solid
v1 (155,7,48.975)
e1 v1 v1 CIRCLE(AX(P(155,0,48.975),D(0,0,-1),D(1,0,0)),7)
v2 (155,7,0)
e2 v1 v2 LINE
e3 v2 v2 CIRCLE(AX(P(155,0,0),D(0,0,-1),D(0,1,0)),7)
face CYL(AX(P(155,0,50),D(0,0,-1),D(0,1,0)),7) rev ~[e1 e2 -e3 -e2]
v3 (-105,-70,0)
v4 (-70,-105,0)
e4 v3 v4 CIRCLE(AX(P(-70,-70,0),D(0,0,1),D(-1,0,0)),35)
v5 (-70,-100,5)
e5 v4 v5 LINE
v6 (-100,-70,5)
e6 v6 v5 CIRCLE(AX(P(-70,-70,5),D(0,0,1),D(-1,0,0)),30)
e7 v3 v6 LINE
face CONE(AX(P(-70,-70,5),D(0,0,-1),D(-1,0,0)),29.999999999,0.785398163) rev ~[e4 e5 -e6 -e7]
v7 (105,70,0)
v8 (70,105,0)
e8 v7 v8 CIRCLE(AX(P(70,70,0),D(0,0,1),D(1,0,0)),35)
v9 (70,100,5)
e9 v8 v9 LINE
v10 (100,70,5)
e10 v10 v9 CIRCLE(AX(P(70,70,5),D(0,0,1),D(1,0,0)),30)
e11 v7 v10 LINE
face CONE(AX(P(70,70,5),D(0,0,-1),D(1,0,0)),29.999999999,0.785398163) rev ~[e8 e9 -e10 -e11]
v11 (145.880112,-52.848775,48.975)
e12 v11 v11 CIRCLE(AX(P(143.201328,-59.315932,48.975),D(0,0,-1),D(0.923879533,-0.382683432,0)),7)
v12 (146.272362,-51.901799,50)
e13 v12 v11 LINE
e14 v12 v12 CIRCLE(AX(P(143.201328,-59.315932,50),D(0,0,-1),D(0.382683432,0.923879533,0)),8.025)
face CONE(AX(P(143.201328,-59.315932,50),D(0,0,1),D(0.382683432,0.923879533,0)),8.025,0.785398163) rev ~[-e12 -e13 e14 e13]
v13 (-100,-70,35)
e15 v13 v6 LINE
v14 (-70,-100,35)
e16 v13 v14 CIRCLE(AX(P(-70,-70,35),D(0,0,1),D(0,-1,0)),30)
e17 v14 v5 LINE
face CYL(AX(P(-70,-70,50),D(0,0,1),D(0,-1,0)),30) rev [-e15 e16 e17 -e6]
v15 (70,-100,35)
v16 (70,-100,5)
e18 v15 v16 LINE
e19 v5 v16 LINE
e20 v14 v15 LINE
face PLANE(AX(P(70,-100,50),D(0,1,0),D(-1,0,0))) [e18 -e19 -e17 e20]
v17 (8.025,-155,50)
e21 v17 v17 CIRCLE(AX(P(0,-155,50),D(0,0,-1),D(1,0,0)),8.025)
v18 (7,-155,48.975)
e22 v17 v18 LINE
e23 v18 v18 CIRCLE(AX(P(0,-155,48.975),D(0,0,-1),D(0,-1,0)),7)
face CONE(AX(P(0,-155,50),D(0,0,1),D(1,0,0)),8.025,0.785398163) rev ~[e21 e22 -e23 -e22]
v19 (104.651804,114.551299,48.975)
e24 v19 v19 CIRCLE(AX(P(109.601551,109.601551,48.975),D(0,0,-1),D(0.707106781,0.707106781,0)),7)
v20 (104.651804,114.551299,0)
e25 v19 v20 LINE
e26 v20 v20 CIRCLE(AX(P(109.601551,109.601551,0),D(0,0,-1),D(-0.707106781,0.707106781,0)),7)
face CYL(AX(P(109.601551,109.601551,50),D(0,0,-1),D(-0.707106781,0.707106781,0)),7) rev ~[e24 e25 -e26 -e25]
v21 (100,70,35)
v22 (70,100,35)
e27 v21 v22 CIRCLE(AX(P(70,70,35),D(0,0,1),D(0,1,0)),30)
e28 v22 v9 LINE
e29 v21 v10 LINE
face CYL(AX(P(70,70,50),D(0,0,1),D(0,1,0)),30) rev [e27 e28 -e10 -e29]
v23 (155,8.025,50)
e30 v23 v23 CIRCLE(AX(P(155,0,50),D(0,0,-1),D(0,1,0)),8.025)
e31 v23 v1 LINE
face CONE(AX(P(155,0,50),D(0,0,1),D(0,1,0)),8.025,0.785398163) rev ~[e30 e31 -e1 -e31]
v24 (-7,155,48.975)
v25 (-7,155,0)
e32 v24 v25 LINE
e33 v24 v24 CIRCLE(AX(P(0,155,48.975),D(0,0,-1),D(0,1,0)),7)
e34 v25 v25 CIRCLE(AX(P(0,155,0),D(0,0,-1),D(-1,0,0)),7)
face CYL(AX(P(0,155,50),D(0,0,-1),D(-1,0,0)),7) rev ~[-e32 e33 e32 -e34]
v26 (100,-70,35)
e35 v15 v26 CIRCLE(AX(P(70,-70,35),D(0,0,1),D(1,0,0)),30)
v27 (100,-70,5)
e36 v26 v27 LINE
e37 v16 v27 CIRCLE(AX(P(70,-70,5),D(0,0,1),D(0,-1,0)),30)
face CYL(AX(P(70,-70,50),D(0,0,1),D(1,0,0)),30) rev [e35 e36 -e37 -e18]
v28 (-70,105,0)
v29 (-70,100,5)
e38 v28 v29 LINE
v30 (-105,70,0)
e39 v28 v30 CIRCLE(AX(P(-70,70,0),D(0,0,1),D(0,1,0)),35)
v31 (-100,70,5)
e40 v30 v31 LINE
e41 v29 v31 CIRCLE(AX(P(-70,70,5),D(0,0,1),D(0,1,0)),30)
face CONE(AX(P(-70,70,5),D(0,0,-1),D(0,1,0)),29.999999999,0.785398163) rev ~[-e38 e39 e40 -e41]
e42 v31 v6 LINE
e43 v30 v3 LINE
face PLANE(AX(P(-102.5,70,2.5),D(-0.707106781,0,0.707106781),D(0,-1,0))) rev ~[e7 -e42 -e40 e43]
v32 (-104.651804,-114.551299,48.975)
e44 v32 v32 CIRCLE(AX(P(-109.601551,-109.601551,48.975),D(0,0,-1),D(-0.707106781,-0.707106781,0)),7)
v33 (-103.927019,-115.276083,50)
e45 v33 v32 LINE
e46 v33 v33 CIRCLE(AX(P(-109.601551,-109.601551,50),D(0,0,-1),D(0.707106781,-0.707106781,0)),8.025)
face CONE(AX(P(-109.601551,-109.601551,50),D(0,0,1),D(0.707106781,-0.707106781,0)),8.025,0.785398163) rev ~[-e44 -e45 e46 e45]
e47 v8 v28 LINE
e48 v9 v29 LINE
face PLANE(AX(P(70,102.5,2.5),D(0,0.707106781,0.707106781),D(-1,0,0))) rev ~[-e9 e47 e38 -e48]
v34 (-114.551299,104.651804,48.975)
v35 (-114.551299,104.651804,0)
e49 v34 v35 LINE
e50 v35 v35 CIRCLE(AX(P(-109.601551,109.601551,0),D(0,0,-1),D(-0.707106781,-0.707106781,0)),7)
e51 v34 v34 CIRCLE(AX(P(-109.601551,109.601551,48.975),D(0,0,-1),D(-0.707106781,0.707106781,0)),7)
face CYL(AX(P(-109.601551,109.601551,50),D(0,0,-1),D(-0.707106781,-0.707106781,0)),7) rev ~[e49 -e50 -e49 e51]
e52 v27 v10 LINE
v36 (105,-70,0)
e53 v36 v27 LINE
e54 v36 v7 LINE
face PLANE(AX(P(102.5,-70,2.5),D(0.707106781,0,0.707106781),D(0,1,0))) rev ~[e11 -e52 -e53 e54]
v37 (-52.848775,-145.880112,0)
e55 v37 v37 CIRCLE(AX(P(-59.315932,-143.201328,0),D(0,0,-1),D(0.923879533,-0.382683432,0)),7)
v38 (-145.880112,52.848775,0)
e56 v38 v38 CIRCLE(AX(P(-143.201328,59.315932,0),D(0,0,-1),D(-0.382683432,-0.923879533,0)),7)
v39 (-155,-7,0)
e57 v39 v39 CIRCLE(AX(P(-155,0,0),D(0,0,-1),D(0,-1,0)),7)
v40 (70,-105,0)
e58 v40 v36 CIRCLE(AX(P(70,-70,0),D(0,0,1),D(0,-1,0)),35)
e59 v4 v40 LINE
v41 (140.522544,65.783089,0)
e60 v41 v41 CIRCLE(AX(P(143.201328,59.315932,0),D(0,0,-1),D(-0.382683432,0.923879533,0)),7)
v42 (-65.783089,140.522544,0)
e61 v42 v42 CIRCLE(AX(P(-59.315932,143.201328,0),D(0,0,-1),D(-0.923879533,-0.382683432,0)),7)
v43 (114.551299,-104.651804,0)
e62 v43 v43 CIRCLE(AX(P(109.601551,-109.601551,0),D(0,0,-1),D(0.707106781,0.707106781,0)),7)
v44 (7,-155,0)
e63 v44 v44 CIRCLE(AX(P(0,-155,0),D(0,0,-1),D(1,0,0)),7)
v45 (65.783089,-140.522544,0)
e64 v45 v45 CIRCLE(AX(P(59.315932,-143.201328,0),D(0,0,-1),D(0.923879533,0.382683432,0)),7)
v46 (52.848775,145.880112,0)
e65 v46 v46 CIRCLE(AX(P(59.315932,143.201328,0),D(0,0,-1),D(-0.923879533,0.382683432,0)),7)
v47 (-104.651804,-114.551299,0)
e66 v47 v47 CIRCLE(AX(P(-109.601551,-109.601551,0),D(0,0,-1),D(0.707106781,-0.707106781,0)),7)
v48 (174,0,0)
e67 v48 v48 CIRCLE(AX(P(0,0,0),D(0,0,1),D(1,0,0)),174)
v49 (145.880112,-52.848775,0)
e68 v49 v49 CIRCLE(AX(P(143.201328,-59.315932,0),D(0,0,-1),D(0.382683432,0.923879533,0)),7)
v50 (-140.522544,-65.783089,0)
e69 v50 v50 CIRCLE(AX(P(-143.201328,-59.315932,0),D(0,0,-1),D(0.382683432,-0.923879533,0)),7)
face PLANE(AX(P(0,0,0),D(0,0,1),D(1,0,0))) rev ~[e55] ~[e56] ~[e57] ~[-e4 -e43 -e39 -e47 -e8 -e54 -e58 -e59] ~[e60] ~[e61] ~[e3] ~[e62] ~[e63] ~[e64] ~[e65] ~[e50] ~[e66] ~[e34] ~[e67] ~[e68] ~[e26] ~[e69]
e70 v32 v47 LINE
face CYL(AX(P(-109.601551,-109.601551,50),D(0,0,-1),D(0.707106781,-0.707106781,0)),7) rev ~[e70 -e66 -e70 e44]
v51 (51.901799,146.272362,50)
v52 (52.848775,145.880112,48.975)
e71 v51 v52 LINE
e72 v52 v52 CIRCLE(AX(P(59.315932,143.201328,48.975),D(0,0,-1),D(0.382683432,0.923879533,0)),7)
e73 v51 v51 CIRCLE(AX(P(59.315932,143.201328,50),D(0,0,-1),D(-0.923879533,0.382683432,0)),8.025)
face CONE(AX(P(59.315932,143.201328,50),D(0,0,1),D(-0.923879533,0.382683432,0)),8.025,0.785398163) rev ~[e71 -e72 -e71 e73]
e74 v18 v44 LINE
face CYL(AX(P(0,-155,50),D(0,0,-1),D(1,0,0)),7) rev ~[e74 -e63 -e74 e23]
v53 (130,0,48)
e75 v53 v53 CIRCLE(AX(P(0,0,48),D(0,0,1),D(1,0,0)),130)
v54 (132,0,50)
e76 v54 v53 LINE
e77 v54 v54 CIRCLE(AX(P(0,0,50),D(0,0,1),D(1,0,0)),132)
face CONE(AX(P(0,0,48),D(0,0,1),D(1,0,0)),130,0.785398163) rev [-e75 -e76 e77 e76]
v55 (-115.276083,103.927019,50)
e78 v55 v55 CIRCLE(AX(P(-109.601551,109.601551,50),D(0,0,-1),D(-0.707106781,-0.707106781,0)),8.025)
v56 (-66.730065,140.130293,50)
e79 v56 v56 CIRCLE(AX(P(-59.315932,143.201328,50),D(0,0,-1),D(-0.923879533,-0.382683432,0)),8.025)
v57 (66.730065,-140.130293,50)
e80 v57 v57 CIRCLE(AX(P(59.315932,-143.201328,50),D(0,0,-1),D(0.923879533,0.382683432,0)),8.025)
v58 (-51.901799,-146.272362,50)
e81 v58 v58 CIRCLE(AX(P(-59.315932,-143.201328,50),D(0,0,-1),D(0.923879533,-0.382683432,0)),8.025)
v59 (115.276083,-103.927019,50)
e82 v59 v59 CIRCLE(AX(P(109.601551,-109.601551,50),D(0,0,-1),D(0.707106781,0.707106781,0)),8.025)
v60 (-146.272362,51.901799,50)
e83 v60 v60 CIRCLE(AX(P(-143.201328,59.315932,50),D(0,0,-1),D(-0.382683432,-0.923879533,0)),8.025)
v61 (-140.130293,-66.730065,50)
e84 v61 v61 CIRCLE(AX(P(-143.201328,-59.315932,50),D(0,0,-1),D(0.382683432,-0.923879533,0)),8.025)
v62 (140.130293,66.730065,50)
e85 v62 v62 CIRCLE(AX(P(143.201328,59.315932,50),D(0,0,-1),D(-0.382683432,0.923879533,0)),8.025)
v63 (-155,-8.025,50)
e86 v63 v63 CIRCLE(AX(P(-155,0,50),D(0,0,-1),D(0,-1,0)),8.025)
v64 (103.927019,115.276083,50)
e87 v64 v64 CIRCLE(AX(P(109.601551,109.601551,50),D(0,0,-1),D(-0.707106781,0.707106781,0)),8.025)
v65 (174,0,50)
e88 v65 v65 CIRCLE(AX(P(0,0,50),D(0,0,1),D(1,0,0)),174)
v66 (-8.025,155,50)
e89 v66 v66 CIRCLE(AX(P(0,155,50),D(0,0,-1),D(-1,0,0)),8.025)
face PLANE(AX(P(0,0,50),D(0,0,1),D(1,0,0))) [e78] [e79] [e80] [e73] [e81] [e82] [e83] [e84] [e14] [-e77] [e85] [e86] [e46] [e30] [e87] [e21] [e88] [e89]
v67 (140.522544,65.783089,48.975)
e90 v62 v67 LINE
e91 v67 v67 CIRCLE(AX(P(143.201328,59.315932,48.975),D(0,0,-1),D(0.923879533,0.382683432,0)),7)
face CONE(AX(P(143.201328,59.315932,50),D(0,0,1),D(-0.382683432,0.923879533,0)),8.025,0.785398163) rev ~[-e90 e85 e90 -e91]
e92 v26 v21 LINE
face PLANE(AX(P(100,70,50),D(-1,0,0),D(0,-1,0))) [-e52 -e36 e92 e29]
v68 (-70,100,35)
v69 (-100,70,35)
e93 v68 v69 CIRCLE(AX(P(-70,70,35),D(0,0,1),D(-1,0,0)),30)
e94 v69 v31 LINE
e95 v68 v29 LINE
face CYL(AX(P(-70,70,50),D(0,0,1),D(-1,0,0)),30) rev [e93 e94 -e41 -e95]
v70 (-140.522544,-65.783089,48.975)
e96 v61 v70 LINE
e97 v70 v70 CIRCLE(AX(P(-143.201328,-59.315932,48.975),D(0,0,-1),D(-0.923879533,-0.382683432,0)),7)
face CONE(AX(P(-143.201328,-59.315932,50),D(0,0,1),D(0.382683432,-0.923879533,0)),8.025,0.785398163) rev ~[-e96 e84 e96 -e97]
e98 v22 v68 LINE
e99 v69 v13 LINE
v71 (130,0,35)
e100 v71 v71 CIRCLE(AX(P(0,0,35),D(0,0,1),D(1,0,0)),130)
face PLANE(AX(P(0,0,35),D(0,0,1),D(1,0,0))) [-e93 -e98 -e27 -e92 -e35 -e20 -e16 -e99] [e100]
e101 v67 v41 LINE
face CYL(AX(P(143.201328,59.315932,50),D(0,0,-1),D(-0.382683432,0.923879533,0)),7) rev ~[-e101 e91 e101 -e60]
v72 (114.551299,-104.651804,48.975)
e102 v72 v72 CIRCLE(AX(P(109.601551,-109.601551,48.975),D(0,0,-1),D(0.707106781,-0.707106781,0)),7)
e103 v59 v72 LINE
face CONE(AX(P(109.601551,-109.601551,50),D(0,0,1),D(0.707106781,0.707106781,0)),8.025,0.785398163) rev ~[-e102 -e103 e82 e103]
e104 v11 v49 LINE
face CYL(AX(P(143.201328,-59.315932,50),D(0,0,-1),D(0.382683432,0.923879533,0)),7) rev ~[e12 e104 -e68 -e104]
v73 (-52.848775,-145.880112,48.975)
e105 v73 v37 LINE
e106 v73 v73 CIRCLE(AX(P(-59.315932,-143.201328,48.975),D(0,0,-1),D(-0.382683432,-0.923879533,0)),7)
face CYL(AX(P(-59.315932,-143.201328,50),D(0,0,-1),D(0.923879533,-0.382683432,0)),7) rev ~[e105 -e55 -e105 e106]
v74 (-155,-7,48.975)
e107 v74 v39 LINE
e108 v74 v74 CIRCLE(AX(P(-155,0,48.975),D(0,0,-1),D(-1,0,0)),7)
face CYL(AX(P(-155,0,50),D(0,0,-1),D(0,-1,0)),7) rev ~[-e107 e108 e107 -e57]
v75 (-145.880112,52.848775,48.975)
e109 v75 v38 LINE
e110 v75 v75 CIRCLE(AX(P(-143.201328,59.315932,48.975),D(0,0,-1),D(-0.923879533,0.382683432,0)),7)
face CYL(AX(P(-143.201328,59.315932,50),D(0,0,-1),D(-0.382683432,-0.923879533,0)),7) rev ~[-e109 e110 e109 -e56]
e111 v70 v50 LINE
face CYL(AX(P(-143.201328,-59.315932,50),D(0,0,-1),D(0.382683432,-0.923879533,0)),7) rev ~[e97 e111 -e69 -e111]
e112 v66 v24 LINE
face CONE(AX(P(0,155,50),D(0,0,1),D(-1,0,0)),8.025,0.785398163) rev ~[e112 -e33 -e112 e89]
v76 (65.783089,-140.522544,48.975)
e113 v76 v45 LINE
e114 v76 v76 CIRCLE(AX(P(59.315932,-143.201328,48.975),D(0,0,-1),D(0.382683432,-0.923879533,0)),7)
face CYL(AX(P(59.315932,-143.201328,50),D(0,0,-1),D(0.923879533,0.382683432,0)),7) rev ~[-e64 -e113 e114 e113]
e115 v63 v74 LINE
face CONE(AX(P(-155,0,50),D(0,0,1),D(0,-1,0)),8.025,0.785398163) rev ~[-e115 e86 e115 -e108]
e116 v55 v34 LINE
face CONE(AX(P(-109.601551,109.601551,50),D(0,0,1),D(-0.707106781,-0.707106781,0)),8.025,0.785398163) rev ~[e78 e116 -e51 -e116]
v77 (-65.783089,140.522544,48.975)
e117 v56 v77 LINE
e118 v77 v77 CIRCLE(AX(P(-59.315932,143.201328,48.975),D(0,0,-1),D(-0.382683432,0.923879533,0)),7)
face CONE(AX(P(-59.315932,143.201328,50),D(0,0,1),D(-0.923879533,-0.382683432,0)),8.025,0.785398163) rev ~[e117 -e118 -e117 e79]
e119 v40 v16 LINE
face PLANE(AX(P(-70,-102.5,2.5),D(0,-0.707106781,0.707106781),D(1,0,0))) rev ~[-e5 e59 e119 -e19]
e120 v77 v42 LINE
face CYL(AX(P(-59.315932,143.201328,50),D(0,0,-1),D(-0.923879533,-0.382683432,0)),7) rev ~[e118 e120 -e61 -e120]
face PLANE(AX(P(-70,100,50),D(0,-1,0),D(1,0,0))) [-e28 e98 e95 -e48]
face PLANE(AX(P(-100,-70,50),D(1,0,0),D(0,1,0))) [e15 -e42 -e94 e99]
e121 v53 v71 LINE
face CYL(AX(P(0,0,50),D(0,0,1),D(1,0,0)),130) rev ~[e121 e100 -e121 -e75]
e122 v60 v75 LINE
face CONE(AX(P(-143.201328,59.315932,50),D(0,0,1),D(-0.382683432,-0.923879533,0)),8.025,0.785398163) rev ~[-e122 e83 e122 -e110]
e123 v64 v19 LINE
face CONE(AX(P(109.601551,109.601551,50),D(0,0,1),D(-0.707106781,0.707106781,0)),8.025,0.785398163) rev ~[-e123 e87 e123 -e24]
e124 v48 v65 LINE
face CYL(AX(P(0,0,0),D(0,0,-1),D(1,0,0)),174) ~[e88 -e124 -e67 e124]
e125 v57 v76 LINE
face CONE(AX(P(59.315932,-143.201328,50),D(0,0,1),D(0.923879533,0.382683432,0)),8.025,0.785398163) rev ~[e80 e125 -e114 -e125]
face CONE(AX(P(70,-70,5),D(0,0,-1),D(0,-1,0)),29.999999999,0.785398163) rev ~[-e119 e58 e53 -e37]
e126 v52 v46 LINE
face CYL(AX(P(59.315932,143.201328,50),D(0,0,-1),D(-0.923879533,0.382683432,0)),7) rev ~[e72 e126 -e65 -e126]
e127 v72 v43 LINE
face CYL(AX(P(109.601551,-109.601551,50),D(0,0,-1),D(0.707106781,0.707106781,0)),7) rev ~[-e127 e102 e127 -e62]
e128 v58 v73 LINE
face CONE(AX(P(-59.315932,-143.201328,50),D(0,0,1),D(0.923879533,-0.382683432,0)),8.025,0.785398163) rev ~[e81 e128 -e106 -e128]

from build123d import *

# Parameters (mm, degrees)
SKETCH_1_R                    = 174
EXTRUDE_1_DEPTH               = 50
CUT_EXTRUDE_1_DEPTH           = 252.101573074
HOLE_WIZARD_M16_1_D           = 14
HOLE_WIZARD_M16_1_CSINK_D     = 16.05
HOLE_WIZARD_M16_1_CSINK_ANGLE = 90
PATTERN_CIRCULAR_1_COUNT      = 16
SKETCH_5_R                    = 130
CUT_EXTRUDE_2_DEPTH           = 15
CHAMFER_1_SIZE                = 2
CHAMFER_2_SIZE                = 5


with BuildPart() as part:
    # 草图1 → 凸台-拉伸1 (new body)
    with BuildSketch(Plane.XY):
        Circle(SKETCH_1_R)
    extrude(amount=EXTRUDE_1_DEPTH)

    # 草图2 → 切除-拉伸1 (cut, through all)
    with BuildSketch(Plane.XY.offset(50)):
        with BuildLine():
            Line((-70, 100), (70, 100))
            ThreePointArc((70, 100), (91.213203436, 91.213203436), (100, 70))
            Line((100, 70), (100, -70))
            ThreePointArc((100, -70), (91.213203436, -91.213203436), (70, -100))
            Line((70, -100), (-70, -100))
            ThreePointArc((-70, -100), (-91.213203436, -91.213203436), (-100, -70))
            Line((-100, -70), (-100, 70))
            ThreePointArc((-100, 70), (-91.213203436, 91.213203436), (-70, 100))
        make_face()
    extrude(amount=-CUT_EXTRUDE_1_DEPTH, mode=Mode.SUBTRACT)

    # M16 螺纹孔1 (through all)
    with Locations(Plane(origin=(0, 155, 50), x_dir=(1, 0, 0), z_dir=(0, 0, 1))):
        with Locations((0, 0)):
            hole_wizard_m16_1 = CounterSinkHole(HOLE_WIZARD_M16_1_D / 2, HOLE_WIZARD_M16_1_CSINK_D / 2, counter_sink_angle=HOLE_WIZARD_M16_1_CSINK_ANGLE)

    # 阵列(圆周)1: M16 螺纹孔1 ×16 about axis
    pattern_circular_1_axis = Axis((0, 0, 0), (0, 0, 1))
    for i in range(1, PATTERN_CIRCULAR_1_COUNT):
        add(hole_wizard_m16_1.rotate(pattern_circular_1_axis, i * 360 / PATTERN_CIRCULAR_1_COUNT), mode=Mode.SUBTRACT)

    # 草图5 → 切除-拉伸2 (cut)
    with BuildSketch(Plane.XY.offset(50)):
        Circle(SKETCH_5_R)
    extrude(amount=-CUT_EXTRUDE_2_DEPTH, mode=Mode.SUBTRACT)

    # 倒角1
    chamfer_1_edges = [part.edges().sort_by_distance(p)[0] for p in [
        (-130, 0, 50),
    ]]
    chamfer(chamfer_1_edges, length=CHAMFER_1_SIZE)

    # 倒角2
    chamfer_2_edges = [part.edges().sort_by_distance(p)[0] for p in [
        (-91.213203436, -91.213203436, 0),
        (-100, 0, 0),
        (-91.213203436, 91.213203436, 0),
        (0, 100, 0),
        (91.213203436, 91.213203436, 0),
        (100, 0, 0),
        (91.213203436, -91.213203436, 0),
        (0, -100, 0),
    ]]
    chamfer(chamfer_2_edges, length=CHAMFER_2_SIZE)


solid = part.part
